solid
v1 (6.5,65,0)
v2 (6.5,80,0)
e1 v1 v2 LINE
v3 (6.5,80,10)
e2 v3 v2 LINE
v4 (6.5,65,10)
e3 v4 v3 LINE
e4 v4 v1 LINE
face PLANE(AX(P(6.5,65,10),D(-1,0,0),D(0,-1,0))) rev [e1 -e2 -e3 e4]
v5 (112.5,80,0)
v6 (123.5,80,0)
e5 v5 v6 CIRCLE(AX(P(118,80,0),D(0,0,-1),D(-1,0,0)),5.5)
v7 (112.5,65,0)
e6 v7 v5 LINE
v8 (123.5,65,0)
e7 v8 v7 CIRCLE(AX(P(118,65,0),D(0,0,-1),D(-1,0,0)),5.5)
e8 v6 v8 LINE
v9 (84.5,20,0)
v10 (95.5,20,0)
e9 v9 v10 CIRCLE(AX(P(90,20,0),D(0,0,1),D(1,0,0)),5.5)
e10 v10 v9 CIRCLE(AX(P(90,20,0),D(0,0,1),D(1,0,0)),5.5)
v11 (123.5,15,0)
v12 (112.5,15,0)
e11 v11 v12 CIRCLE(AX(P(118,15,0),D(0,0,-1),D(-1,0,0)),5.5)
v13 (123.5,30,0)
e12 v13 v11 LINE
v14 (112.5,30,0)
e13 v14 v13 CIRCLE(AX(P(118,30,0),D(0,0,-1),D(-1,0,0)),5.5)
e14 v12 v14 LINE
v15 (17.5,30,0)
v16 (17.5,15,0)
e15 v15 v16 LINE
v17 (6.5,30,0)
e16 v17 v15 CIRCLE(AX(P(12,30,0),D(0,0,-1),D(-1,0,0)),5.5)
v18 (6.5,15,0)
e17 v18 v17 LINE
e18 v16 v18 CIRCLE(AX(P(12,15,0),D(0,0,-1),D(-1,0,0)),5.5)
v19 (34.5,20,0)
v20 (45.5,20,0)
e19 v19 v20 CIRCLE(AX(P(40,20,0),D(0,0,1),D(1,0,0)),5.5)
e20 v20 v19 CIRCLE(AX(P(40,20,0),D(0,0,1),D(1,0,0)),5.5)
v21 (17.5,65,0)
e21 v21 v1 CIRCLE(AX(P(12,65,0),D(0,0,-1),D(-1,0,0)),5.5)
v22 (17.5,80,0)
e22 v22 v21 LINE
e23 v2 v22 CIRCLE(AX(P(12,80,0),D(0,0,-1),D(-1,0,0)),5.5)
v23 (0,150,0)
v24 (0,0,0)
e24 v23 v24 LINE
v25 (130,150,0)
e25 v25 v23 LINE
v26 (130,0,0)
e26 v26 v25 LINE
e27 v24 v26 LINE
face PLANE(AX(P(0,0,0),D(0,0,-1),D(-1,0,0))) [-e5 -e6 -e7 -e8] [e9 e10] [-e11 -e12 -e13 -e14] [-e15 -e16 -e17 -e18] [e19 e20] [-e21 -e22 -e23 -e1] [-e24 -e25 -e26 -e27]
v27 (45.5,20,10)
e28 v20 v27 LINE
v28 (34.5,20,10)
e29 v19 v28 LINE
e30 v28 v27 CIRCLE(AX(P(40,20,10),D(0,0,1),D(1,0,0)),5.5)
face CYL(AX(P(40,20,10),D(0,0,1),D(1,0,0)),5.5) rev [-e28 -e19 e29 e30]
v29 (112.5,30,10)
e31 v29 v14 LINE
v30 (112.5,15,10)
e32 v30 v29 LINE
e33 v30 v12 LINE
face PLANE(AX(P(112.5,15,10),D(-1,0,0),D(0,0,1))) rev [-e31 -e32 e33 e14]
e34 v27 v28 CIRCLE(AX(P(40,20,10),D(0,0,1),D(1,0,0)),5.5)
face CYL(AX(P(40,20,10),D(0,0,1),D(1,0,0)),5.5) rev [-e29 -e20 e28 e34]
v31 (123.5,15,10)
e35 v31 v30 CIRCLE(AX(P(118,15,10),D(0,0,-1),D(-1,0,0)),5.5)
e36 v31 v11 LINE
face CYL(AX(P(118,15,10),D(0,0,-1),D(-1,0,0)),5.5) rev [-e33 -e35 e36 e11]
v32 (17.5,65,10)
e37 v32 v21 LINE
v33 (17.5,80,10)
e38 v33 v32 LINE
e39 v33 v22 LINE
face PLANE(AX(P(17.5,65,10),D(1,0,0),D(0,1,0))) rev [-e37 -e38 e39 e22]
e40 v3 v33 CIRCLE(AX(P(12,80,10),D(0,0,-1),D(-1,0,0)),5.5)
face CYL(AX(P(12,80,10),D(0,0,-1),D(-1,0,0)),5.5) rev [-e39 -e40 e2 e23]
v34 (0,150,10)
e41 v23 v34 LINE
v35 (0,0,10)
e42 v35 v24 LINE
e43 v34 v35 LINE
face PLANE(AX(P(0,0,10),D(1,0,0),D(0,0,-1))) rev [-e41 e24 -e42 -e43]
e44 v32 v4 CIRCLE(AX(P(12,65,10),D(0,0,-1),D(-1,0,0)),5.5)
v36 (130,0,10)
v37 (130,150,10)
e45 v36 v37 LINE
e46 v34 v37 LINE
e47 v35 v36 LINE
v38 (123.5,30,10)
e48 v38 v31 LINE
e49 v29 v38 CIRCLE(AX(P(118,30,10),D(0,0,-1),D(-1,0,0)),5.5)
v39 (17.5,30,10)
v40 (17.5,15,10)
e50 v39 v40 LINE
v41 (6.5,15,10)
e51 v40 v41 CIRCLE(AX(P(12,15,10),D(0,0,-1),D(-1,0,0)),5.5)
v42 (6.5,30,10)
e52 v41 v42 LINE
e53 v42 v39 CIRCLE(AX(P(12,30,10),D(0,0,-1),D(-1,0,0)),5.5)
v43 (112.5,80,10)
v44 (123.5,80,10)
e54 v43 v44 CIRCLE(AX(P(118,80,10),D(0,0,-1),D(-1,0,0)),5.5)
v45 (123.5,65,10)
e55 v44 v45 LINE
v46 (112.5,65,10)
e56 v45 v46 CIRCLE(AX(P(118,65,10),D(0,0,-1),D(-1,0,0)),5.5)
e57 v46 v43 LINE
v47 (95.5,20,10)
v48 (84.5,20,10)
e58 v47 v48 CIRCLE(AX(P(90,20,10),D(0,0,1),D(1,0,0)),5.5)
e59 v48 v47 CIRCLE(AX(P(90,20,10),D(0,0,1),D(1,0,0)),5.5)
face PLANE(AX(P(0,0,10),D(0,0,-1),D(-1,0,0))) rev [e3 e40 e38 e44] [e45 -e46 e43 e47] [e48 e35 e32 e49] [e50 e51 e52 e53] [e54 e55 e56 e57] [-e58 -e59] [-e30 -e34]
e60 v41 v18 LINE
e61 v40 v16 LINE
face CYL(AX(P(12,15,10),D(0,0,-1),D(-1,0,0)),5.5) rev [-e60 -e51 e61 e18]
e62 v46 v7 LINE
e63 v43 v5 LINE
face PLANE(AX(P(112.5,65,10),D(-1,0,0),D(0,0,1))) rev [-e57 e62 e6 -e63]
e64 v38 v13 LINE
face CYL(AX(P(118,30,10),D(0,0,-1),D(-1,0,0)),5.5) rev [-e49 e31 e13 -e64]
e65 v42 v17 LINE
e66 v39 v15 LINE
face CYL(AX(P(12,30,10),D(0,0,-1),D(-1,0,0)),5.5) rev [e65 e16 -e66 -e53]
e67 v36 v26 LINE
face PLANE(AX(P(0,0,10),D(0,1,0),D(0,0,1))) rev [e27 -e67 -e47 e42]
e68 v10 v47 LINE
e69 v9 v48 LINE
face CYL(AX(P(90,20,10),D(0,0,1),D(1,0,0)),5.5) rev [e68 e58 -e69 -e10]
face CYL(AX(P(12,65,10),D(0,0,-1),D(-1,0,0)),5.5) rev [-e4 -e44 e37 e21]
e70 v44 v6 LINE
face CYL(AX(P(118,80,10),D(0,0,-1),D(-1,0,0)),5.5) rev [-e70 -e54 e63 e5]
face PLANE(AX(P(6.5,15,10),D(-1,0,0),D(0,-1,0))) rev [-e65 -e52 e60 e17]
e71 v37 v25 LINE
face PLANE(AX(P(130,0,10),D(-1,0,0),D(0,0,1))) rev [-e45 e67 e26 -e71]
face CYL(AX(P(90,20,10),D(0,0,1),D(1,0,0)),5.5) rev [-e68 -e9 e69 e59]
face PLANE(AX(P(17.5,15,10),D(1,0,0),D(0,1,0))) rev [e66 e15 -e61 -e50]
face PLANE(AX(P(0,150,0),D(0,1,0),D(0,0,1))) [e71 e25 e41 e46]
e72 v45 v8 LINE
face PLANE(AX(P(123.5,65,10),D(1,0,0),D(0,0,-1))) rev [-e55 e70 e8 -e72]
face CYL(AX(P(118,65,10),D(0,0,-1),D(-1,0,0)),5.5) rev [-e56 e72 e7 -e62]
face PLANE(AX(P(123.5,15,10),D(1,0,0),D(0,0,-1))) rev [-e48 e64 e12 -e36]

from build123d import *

# Parameters (mm, degrees)
SKETCH1_W                  = 130
SKETCH1_H                  = 130
BOSS_EXTRUDE1_DEPTH        = 10
F_11_0_11_DIAMETER_HOLE1_D = 11
SKETCH4_W                  = 130
SKETCH4_H                  = 10
BOSS_EXTRUDE2_DEPTH        = 20
M6_CLEARANCE_HOLE1_D       = 7
CUT_EXTRUDE1_DEPTH         = 199.746069144


with BuildPart() as part:
    # Sketch1 → Boss-Extrude1 (new body)
    with BuildSketch(Plane.XY):
        with Locations((65, 65)):
            Rectangle(SKETCH1_W, SKETCH1_H)
    extrude(amount=BOSS_EXTRUDE1_DEPTH)

    # Ø11.0 (11) Diameter Hole1 (through all)
    with Locations(Plane.XY.offset(10)):
        with Locations((40, 20), (90, 20)):
            Hole(F_11_0_11_DIAMETER_HOLE1_D / 2)

    # Sketch4 → Boss-Extrude2 (add)
    with BuildSketch(Plane(origin=(0, 130, 0), x_dir=(1, 0, 0), z_dir=(0, 1, 0))):
        with Locations((65, -5)):
            Rectangle(SKETCH4_W, SKETCH4_H)
    extrude(amount=BOSS_EXTRUDE2_DEPTH)

    # M6 Clearance Hole1 (through all)
    with Locations(Plane(origin=(0, 0, 0), x_dir=(-1, 0, 0), z_dir=(0, 0, -1))):
        with Locations((-118, 68.5), (-118, 18.5), (-12, 68.5), (-12, 18.5)):
            Hole(M6_CLEARANCE_HOLE1_D / 2)

    # Sketch8 → Cut-Extrude1 (cut, through all)
    with BuildSketch(Plane(origin=(0, 0, 0), x_dir=(-1, 0, 0), z_dir=(0, 0, -1))):
        with BuildLine():
            Line((-123.5, 15), (-123.5, 30))
            ThreePointArc((-123.5, 30), (-118, 35.5), (-112.5, 30))
            Line((-112.5, 30), (-112.5, 15))
            ThreePointArc((-112.5, 15), (-118, 9.5), (-123.5, 15))
        make_face()
        with BuildLine():
            Line((-123.5, 65), (-123.5, 80))
            ThreePointArc((-123.5, 80), (-118, 85.5), (-112.5, 80))
            Line((-112.5, 80), (-112.5, 65))
            ThreePointArc((-112.5, 65), (-118, 59.5), (-123.5, 65))
        make_face()
        with BuildLine():
            Line((-17.5, 65), (-17.5, 80))
            ThreePointArc((-17.5, 80), (-12, 85.5), (-6.5, 80))
            Line((-6.5, 80), (-6.5, 65))
            ThreePointArc((-6.5, 65), (-12, 59.5), (-17.5, 65))
        make_face()
        with BuildLine():
            Line((-17.5, 15), (-17.5, 30))
            ThreePointArc((-17.5, 30), (-12, 35.5), (-6.5, 30))
            Line((-6.5, 30), (-6.5, 15))
            ThreePointArc((-6.5, 15), (-12, 9.5), (-17.5, 15))
        make_face()
    extrude(amount=-CUT_EXTRUDE1_DEPTH, mode=Mode.SUBTRACT)


solid = part.part
